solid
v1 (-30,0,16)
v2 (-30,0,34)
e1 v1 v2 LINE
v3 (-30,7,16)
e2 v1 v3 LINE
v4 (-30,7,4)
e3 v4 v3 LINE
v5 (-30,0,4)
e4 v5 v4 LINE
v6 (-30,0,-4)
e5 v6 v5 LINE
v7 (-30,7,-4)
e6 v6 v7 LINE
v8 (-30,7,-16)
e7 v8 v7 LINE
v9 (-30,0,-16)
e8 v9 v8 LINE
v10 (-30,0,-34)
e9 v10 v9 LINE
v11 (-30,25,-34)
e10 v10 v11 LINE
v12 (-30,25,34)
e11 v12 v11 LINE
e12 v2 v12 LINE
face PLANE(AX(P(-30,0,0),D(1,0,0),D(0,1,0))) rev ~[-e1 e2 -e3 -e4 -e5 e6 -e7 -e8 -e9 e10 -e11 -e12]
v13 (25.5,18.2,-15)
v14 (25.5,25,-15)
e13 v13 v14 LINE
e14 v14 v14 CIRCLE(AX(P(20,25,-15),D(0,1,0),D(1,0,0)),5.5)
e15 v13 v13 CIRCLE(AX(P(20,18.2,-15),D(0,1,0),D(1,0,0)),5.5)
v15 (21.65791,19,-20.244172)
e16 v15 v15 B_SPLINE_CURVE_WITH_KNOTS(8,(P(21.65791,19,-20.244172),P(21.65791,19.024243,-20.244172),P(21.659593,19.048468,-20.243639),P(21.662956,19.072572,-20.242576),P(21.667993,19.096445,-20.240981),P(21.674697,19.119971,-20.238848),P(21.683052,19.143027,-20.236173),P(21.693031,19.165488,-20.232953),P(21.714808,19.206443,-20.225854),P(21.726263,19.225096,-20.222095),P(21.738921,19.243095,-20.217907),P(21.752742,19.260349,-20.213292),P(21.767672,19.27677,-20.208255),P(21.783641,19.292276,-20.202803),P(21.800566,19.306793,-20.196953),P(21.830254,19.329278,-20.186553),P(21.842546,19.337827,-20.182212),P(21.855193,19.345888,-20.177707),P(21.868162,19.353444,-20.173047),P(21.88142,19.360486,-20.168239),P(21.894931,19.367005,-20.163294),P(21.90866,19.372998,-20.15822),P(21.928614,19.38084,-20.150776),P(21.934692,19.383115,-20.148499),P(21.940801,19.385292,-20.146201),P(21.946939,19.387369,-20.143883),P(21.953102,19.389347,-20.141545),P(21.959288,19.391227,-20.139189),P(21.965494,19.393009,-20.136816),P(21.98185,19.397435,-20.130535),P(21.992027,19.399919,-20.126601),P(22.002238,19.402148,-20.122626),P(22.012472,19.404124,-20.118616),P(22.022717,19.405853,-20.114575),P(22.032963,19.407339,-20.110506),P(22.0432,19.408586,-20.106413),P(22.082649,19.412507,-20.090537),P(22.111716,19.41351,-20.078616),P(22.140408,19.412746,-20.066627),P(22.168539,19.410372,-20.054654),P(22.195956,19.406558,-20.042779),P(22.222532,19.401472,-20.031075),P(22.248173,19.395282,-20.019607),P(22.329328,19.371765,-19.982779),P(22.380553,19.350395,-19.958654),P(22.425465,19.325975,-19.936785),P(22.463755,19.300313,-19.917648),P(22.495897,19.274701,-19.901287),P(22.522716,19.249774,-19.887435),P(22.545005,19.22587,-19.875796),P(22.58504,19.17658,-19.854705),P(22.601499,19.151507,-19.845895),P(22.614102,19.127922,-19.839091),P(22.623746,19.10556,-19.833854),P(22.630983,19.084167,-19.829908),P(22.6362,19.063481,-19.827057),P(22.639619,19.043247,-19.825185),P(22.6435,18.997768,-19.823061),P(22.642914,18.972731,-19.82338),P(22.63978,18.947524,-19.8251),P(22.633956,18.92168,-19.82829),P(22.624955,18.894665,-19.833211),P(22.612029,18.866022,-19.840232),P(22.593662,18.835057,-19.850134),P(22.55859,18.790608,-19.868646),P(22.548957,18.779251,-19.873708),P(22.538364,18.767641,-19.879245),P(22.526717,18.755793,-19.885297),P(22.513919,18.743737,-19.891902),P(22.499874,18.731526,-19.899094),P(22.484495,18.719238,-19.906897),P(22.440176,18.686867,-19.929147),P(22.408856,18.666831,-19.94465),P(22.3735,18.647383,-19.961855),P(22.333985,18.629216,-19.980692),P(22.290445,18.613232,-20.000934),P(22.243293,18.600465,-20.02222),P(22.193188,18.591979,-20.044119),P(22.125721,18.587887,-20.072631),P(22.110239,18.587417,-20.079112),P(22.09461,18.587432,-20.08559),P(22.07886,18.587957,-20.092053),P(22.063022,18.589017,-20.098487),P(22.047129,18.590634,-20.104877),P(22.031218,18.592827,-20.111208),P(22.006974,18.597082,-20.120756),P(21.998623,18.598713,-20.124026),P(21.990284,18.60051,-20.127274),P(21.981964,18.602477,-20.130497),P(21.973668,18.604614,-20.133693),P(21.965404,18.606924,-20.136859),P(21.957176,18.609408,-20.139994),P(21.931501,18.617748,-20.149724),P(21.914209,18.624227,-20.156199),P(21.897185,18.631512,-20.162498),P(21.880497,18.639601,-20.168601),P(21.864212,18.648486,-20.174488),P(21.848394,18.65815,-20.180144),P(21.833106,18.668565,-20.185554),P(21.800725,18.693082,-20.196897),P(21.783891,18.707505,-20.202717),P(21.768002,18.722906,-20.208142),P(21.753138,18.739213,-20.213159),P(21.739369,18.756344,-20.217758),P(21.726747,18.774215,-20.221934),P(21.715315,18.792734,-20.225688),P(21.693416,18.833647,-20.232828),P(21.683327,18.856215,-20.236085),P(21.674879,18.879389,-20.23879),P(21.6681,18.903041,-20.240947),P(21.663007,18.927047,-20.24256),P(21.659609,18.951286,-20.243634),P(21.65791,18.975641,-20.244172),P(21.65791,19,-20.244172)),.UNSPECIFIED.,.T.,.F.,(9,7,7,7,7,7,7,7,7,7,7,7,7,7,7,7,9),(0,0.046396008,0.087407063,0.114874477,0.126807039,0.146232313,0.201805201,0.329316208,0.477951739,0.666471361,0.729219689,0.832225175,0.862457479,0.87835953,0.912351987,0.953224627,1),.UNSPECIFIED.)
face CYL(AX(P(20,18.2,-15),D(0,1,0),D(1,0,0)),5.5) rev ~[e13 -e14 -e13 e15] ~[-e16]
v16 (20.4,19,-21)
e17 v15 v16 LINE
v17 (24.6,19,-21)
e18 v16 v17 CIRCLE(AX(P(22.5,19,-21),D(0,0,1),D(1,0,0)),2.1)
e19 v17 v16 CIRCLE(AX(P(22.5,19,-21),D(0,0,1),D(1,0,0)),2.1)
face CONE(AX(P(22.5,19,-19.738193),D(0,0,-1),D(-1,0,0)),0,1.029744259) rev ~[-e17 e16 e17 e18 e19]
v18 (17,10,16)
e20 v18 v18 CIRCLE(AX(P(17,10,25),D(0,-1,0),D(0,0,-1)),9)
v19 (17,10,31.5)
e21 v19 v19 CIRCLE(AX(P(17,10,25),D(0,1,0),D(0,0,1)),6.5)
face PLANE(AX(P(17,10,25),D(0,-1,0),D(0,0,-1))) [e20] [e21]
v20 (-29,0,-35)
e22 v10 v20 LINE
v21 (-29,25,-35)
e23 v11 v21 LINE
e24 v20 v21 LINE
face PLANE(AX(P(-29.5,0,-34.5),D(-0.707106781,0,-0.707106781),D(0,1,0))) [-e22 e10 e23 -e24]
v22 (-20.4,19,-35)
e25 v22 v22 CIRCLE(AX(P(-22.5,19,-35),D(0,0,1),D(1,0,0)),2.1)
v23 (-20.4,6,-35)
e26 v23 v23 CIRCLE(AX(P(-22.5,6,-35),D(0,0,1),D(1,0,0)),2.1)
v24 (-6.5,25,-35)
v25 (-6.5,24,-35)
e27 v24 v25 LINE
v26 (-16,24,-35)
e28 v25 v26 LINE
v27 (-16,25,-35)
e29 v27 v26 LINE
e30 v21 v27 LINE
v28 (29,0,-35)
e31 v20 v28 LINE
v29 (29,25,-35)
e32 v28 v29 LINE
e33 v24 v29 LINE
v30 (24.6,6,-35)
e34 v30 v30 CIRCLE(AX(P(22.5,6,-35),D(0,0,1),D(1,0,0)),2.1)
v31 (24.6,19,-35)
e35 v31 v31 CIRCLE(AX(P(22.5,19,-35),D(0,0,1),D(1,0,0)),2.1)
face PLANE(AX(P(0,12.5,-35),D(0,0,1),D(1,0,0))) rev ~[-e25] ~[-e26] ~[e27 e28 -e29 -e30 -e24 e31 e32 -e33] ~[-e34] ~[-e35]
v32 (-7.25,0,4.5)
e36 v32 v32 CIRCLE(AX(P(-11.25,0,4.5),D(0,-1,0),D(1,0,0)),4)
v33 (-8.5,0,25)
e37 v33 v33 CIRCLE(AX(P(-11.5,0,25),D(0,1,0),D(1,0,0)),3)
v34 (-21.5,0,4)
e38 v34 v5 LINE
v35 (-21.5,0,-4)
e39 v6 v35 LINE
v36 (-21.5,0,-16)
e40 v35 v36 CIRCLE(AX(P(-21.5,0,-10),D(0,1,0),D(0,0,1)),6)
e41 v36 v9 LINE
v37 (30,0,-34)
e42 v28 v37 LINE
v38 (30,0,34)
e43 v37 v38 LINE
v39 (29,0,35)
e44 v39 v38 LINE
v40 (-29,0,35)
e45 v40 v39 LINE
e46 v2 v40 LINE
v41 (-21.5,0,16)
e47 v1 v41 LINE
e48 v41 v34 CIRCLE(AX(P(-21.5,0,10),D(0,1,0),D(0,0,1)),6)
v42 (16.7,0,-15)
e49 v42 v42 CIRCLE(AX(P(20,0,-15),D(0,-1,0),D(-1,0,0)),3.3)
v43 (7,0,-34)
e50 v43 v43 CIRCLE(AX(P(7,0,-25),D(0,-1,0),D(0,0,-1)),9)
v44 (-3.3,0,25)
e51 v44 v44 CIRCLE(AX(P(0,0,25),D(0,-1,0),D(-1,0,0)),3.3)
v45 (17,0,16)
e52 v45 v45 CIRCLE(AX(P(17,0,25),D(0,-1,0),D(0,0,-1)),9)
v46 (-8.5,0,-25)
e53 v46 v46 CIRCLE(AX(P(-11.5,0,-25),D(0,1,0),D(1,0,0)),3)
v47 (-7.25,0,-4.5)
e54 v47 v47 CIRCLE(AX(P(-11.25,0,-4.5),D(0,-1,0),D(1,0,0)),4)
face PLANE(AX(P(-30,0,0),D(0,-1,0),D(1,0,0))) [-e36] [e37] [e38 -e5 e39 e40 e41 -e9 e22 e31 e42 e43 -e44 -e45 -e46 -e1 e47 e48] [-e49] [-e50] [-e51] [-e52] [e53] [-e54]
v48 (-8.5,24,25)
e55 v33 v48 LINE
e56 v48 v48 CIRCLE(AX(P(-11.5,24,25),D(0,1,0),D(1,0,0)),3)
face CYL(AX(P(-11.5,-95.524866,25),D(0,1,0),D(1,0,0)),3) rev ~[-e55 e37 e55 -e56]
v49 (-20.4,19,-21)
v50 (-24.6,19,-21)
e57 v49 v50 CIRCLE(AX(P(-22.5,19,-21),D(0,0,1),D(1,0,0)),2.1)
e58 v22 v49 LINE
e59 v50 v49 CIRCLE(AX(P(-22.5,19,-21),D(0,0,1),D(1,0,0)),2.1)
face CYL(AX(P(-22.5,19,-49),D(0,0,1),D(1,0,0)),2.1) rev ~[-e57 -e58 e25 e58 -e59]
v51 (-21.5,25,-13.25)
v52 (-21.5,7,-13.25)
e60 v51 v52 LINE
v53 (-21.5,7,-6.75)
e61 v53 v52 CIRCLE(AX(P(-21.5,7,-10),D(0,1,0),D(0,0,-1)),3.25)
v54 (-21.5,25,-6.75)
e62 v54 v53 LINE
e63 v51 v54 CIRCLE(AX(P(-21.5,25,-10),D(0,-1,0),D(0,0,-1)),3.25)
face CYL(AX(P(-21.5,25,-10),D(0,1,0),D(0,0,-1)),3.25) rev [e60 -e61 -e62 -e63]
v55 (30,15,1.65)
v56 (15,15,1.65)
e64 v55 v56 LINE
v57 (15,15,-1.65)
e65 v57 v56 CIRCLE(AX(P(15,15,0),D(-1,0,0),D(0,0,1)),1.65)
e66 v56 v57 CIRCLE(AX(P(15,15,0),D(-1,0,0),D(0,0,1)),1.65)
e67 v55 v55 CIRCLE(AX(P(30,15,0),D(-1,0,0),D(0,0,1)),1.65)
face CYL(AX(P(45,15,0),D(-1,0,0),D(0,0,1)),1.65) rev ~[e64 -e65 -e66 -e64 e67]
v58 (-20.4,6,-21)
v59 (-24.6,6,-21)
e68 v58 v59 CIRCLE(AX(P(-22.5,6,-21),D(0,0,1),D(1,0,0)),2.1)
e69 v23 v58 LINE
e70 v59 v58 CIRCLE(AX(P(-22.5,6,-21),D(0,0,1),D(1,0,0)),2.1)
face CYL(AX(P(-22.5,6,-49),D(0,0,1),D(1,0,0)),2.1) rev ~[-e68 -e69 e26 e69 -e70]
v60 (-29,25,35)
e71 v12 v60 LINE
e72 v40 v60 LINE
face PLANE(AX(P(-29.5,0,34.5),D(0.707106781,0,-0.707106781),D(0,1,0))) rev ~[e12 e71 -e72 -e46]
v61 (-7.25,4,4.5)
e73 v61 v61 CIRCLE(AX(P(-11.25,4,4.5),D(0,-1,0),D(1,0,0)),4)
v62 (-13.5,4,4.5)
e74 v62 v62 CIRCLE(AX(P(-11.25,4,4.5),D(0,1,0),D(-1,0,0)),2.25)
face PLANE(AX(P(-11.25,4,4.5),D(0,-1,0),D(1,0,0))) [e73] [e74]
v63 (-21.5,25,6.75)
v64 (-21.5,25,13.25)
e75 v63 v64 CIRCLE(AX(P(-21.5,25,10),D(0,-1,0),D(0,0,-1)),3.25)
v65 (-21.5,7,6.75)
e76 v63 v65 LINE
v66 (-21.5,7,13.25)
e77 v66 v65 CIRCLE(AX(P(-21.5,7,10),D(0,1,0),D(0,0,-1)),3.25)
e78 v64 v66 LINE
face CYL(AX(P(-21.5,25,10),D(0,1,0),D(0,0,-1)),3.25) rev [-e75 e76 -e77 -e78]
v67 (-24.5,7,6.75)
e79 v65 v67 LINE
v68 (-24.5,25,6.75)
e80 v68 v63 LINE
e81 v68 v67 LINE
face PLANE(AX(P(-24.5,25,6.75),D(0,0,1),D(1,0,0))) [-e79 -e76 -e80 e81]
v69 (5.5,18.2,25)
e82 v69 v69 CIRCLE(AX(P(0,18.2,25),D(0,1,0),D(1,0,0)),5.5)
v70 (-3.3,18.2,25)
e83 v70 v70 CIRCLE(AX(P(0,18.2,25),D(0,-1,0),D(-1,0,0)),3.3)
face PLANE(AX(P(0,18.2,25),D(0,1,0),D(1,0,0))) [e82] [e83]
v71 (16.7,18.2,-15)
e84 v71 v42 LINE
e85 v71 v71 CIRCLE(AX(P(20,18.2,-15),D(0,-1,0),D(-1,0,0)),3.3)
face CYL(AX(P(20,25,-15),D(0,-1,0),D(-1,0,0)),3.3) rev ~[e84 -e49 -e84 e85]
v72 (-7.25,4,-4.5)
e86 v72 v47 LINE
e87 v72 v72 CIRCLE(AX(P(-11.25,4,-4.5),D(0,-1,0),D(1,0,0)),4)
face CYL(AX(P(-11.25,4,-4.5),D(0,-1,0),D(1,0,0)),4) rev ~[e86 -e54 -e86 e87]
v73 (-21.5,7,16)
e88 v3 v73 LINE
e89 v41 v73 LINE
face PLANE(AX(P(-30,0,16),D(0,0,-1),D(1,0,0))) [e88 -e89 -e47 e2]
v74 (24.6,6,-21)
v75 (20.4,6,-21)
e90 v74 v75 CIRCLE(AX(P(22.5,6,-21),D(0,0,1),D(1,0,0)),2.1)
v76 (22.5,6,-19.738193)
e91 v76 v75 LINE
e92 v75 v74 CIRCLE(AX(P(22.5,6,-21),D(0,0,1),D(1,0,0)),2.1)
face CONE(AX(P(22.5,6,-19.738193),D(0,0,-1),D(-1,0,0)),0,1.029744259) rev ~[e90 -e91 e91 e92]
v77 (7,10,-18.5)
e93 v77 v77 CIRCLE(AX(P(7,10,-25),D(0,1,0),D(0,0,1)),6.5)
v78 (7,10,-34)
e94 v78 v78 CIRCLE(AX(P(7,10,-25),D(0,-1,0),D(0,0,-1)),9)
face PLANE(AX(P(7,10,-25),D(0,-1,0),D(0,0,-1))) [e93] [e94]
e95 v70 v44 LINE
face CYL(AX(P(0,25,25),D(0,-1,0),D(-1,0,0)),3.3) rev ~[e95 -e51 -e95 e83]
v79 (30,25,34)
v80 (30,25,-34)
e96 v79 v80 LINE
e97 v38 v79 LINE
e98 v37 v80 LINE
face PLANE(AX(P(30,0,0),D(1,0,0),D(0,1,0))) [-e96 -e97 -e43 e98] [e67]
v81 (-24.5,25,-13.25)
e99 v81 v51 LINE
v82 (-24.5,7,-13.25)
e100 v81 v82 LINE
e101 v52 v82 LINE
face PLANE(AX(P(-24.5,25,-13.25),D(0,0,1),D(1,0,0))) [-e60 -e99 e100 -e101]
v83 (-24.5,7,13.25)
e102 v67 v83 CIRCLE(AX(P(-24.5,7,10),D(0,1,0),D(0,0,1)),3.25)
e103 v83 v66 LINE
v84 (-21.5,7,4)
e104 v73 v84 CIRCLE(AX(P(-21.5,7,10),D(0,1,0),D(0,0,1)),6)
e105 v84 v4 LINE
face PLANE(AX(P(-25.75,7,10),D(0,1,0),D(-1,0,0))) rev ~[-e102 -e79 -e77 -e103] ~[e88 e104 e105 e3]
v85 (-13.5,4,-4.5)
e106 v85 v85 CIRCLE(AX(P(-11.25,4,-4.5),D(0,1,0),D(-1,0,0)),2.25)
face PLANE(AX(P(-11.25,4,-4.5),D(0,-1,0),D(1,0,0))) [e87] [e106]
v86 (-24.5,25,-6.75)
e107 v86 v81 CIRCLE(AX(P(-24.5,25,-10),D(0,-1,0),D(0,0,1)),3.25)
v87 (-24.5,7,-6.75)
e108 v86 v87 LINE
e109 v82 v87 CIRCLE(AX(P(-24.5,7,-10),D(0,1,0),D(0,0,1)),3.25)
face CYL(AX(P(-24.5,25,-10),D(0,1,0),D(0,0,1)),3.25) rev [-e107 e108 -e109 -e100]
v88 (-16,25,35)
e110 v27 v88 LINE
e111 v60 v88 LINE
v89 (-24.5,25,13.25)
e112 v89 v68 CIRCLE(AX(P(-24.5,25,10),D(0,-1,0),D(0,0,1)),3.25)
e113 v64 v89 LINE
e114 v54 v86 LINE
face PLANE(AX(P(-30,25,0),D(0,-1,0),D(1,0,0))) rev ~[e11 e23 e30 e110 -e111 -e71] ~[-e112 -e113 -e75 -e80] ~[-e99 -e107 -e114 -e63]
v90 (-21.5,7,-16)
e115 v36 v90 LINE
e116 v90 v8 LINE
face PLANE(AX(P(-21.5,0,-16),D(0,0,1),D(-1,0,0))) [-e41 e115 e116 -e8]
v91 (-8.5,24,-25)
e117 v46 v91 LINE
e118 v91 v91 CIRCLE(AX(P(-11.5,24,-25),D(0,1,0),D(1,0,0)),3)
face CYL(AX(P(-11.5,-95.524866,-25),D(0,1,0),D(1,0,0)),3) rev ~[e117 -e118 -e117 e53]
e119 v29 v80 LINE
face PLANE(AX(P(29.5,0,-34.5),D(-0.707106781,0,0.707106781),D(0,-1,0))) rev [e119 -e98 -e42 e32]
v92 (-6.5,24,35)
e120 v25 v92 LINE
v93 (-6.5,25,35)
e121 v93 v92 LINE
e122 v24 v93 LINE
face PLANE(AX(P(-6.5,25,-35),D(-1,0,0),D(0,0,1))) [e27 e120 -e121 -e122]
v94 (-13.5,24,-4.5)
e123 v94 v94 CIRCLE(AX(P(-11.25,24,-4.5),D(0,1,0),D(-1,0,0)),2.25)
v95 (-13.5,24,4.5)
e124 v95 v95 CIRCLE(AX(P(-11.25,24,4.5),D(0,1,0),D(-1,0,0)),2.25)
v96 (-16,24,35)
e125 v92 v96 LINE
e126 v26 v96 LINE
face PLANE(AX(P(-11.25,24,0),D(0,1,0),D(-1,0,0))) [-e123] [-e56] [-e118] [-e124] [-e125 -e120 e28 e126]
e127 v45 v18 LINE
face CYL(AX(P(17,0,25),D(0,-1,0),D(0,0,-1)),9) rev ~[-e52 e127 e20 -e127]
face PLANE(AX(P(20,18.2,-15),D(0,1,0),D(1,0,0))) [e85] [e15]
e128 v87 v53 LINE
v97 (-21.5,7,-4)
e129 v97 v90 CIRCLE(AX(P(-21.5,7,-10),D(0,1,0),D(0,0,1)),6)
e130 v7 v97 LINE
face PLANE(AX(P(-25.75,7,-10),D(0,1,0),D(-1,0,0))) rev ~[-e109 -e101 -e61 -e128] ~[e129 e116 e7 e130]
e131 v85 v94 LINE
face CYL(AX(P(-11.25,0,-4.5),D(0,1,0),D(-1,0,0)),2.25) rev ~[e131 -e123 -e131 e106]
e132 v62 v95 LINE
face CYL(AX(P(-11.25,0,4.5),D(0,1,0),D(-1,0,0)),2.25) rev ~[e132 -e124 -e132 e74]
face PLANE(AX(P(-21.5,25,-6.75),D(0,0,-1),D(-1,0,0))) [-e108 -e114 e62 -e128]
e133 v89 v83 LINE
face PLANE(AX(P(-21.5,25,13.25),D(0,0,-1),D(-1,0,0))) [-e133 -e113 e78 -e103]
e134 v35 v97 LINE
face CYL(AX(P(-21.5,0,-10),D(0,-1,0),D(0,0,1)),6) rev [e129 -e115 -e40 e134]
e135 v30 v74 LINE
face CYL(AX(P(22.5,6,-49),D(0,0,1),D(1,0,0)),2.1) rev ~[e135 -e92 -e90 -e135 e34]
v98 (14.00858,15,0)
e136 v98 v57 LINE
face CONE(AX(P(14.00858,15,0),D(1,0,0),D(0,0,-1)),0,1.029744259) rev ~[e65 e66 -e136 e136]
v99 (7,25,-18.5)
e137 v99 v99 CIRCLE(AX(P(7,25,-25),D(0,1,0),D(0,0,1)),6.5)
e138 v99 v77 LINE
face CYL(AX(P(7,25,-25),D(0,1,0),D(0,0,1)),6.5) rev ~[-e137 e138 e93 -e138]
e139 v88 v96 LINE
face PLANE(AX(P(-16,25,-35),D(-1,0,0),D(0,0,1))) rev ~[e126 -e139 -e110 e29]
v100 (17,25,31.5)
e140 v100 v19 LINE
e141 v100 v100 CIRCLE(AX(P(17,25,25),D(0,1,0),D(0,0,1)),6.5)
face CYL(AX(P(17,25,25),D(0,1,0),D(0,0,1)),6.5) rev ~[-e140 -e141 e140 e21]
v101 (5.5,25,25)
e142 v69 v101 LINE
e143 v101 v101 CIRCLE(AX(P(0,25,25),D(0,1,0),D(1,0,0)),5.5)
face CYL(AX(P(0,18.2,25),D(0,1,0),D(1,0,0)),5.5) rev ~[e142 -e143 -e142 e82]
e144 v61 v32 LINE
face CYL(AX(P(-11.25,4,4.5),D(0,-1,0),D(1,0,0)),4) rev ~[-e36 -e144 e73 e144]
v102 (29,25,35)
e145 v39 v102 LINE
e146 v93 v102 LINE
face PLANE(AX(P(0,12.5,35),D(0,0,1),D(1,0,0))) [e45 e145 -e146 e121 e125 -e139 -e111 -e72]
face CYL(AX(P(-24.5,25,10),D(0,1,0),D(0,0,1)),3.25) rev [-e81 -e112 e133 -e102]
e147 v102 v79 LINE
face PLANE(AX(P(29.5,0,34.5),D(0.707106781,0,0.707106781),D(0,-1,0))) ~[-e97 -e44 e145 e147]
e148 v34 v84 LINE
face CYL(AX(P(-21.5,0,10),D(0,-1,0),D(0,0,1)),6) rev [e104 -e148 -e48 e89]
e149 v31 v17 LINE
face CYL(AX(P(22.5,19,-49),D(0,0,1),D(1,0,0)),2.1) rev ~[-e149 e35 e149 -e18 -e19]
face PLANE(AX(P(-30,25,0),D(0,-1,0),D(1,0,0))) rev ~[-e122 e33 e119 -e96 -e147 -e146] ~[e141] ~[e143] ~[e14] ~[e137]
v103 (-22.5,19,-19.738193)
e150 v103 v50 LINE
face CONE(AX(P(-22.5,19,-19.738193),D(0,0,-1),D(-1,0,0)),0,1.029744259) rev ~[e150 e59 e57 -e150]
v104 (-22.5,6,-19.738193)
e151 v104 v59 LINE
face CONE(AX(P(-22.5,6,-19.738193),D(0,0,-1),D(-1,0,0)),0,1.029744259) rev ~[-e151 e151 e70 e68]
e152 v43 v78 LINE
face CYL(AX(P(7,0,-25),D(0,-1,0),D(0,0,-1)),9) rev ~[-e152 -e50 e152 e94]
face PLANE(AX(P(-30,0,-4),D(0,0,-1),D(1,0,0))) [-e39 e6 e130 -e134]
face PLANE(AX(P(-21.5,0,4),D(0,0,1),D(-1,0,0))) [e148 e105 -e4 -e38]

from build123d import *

# Parameters (mm, degrees)
SKETCH1_W                                            = 60
SKETCH1_H                                            = 25
BOSS_EXTRUDE1_DEPTH                                  = 35
SKETCH2_R                                            = 6.5
CUT_EXTRUDE1_DEPTH                                   = 53.440442409
SKETCH3_R                                            = 9
CUT_EXTRUDE2_DEPTH                                   = 10
SKETCH6_W                                            = 9.5
SKETCH6_H                                            = 70
CUT_EXTRUDE3_DEPTH                                   = 1
M4_TAPPED_HOLE1_D                                    = 3.3
M4_TAPPED_HOLE1_DEPTH                                = 12
M4_TAPPED_HOLE1_TIP                                  = 0.991420021
CUT_EXTRUDE4_DEPTH                                   = 7
M5_TAPPED_HOLE1_D                                    = 4.2
M5_TAPPED_HOLE1_DEPTH                                = 14
M5_TAPPED_HOLE1_TIP                                  = 1.2618073
HOLE_SIZE_PER_SOCKET_HEAD_CAP_SCREW_TYPE_D           = 4.5
HOLE_SIZE_PER_SOCKET_HEAD_CAP_SCREW_TYPE_CBORE_D     = 8
HOLE_SIZE_PER_SOCKET_HEAD_CAP_SCREW_TYPE_CBORE_DEPTH = 4
F_6_0_6_DIAMETER_HOLE2_D                             = 6
HOLE_SIZE_PER_SOCKET_HEAD_CAP_SCREW_2_D              = 6.6
HOLE_SIZE_PER_SOCKET_HEAD_CAP_SCREW_2_CBORE_D        = 11
HOLE_SIZE_PER_SOCKET_HEAD_CAP_SCREW_2_CBORE_DEPTH    = 6.8
M4_TAPPED_HOLE2_D                                    = 3.3
M4_TAPPED_HOLE2_DEPTH                                = 15
M4_TAPPED_HOLE2_TIP                                  = 0.991420021
CHAMFER1_SIZE                                        = 1


with BuildPart() as part:
    # Sketch1 → Boss-Extrude1 (new, symmetric)
    with BuildSketch(Plane.XY):
        with Locations((0, 12.5)):
            Rectangle(SKETCH1_W, SKETCH1_H)
    extrude(amount=BOSS_EXTRUDE1_DEPTH, both=True)

    # Sketch2 → Cut-Extrude1 (cut, through all)
    with BuildSketch(Plane(origin=(0, 25, 0), x_dir=(1, 0, 0), z_dir=(0, 1, 0))):
        with Locations(Location((7, 25, 0), (0, 0, 270))):
            Circle(SKETCH2_R)
        with Locations(Location((17, -25, 0), (0, 0, 270))):
            Circle(SKETCH2_R)
        with BuildLine():
            Line((-24.5, 13.25), (-21.5, 13.25))
            ThreePointArc((-21.5, 13.25), (-18.25, 10), (-21.5, 6.75))
            Line((-21.5, 6.75), (-24.5, 6.75))
            ThreePointArc((-24.5, 6.75), (-27.75, 10), (-24.5, 13.25))
        make_face()
        with BuildLine():
            Line((-24.5, -6.75), (-21.5, -6.75))
            ThreePointArc((-21.5, -6.75), (-18.25, -10), (-21.5, -13.25))
            Line((-21.5, -13.25), (-24.5, -13.25))
            ThreePointArc((-24.5, -13.25), (-27.75, -10), (-24.5, -6.75))
        make_face()
    extrude(amount=-CUT_EXTRUDE1_DEPTH, mode=Mode.SUBTRACT)

    # Sketch3 → Cut-Extrude2 (cut)
    with BuildSketch(Plane.XZ):
        with Locations(Location((17, 25, 0), (0, 0, 270))):
            Circle(SKETCH3_R)
        with Locations(Location((7, -25, 0), (0, 0, 270))):
            Circle(SKETCH3_R)
    extrude(amount=-CUT_EXTRUDE2_DEPTH, mode=Mode.SUBTRACT)

    # Sketch6 → Cut-Extrude3 (cut)
    with BuildSketch(Plane(origin=(0, 25, 0), x_dir=(-1, 0, 0), z_dir=(0, 1, 0))):
        with Locations((11.25, 0)):
            Rectangle(SKETCH6_W, SKETCH6_H)
    extrude(amount=-CUT_EXTRUDE3_DEPTH, mode=Mode.SUBTRACT)

    # M4 Tapped Hole1
    with Locations(Plane(origin=(0, 24, 0), x_dir=(-1, 0, 0), z_dir=(0, 1, 0))):
        with Locations((11.25, 4.5), (11.25, -4.5)):
            Hole(M4_TAPPED_HOLE1_D / 2, depth=M4_TAPPED_HOLE1_DEPTH)
            with Locations((0, 0, -(M4_TAPPED_HOLE1_DEPTH + M4_TAPPED_HOLE1_TIP / 2))):  # 118° drill point
                Cone(0, M4_TAPPED_HOLE1_D / 2, M4_TAPPED_HOLE1_TIP, mode=Mode.SUBTRACT)

    # Sketch10 → Cut-Extrude4 (cut)
    with BuildSketch(Plane.XZ):
        with BuildLine():
            Line((-21.5, -16), (-30, -16))
            ThreePointArc((-30, -16), (-36, -10), (-30, -4))
            Line((-30, -4), (-21.5, -4))
            ThreePointArc((-21.5, -4), (-15.5, -10), (-21.5, -16))
        make_face()
        with BuildLine():
            Line((-21.5, 4), (-30, 4))
            ThreePointArc((-30, 4), (-36, 10), (-30, 16))
            Line((-30, 16), (-21.5, 16))
            ThreePointArc((-21.5, 16), (-15.5, 10), (-21.5, 4))
        make_face()
    extrude(amount=-CUT_EXTRUDE4_DEPTH, mode=Mode.SUBTRACT)

    # M5 Tapped Hole1
    with Locations(Plane(origin=(0, 0, -35), x_dir=(-1, 0, 0), z_dir=(0, 0, -1))):
        with Locations((-22.5, 19), (-22.5, 6), (22.5, 19), (22.5, 6)):
            Hole(M5_TAPPED_HOLE1_D / 2, depth=M5_TAPPED_HOLE1_DEPTH)
            with Locations((0, 0, -(M5_TAPPED_HOLE1_DEPTH + M5_TAPPED_HOLE1_TIP / 2))):  # 118° drill point
                Cone(0, M5_TAPPED_HOLE1_D / 2, M5_TAPPED_HOLE1_TIP, mode=Mode.SUBTRACT)

    # Hole size per socket head cap screw type (through all)
    with Locations(Plane.XZ):
        with Locations((-11.25, -4.5), (-11.25, 4.5)):
            CounterBoreHole(HOLE_SIZE_PER_SOCKET_HEAD_CAP_SCREW_TYPE_D / 2, HOLE_SIZE_PER_SOCKET_HEAD_CAP_SCREW_TYPE_CBORE_D / 2, HOLE_SIZE_PER_SOCKET_HEAD_CAP_SCREW_TYPE_CBORE_DEPTH)

    # Ø6.0 (6) Diameter Hole2 (through all)
    with Locations(Plane(origin=(0, 0, 0), x_dir=(-1, 0, 0), z_dir=(0, -1, 0))):
        with Locations((11.5, -25), (11.5, 25)):
            Hole(F_6_0_6_DIAMETER_HOLE2_D / 2)

    # Hole size per socket head cap screw  2 (through all)
    with Locations(Plane(origin=(0, 25, 0), x_dir=(1, 0, 0), z_dir=(0, 1, 0))):
        with Locations((0, -25), (20, 15)):
            CounterBoreHole(HOLE_SIZE_PER_SOCKET_HEAD_CAP_SCREW_2_D / 2, HOLE_SIZE_PER_SOCKET_HEAD_CAP_SCREW_2_CBORE_D / 2, HOLE_SIZE_PER_SOCKET_HEAD_CAP_SCREW_2_CBORE_DEPTH)

    # M4 Tapped Hole2
    with Locations(Plane(origin=(30, 0, 0), x_dir=(0, 0, -1), z_dir=(1, 0, 0))):
        with Locations((0, 15)):
            Hole(M4_TAPPED_HOLE2_D / 2, depth=M4_TAPPED_HOLE2_DEPTH)
            with Locations((0, 0, -(M4_TAPPED_HOLE2_DEPTH + M4_TAPPED_HOLE2_TIP / 2))):  # 118° drill point
                Cone(0, M4_TAPPED_HOLE2_D / 2, M4_TAPPED_HOLE2_TIP, mode=Mode.SUBTRACT)

    # Chamfer1
    chamfer1_edges = [part.edges().sort_by_distance(p)[0] for p in [
        (30, 12.5, 35),
        (-30, 12.5, 35),
        (30, 12.5, -35),
        (-30, 12.5, -35),
    ]]
    chamfer(chamfer1_edges, length=CHAMFER1_SIZE)


solid = part.part
